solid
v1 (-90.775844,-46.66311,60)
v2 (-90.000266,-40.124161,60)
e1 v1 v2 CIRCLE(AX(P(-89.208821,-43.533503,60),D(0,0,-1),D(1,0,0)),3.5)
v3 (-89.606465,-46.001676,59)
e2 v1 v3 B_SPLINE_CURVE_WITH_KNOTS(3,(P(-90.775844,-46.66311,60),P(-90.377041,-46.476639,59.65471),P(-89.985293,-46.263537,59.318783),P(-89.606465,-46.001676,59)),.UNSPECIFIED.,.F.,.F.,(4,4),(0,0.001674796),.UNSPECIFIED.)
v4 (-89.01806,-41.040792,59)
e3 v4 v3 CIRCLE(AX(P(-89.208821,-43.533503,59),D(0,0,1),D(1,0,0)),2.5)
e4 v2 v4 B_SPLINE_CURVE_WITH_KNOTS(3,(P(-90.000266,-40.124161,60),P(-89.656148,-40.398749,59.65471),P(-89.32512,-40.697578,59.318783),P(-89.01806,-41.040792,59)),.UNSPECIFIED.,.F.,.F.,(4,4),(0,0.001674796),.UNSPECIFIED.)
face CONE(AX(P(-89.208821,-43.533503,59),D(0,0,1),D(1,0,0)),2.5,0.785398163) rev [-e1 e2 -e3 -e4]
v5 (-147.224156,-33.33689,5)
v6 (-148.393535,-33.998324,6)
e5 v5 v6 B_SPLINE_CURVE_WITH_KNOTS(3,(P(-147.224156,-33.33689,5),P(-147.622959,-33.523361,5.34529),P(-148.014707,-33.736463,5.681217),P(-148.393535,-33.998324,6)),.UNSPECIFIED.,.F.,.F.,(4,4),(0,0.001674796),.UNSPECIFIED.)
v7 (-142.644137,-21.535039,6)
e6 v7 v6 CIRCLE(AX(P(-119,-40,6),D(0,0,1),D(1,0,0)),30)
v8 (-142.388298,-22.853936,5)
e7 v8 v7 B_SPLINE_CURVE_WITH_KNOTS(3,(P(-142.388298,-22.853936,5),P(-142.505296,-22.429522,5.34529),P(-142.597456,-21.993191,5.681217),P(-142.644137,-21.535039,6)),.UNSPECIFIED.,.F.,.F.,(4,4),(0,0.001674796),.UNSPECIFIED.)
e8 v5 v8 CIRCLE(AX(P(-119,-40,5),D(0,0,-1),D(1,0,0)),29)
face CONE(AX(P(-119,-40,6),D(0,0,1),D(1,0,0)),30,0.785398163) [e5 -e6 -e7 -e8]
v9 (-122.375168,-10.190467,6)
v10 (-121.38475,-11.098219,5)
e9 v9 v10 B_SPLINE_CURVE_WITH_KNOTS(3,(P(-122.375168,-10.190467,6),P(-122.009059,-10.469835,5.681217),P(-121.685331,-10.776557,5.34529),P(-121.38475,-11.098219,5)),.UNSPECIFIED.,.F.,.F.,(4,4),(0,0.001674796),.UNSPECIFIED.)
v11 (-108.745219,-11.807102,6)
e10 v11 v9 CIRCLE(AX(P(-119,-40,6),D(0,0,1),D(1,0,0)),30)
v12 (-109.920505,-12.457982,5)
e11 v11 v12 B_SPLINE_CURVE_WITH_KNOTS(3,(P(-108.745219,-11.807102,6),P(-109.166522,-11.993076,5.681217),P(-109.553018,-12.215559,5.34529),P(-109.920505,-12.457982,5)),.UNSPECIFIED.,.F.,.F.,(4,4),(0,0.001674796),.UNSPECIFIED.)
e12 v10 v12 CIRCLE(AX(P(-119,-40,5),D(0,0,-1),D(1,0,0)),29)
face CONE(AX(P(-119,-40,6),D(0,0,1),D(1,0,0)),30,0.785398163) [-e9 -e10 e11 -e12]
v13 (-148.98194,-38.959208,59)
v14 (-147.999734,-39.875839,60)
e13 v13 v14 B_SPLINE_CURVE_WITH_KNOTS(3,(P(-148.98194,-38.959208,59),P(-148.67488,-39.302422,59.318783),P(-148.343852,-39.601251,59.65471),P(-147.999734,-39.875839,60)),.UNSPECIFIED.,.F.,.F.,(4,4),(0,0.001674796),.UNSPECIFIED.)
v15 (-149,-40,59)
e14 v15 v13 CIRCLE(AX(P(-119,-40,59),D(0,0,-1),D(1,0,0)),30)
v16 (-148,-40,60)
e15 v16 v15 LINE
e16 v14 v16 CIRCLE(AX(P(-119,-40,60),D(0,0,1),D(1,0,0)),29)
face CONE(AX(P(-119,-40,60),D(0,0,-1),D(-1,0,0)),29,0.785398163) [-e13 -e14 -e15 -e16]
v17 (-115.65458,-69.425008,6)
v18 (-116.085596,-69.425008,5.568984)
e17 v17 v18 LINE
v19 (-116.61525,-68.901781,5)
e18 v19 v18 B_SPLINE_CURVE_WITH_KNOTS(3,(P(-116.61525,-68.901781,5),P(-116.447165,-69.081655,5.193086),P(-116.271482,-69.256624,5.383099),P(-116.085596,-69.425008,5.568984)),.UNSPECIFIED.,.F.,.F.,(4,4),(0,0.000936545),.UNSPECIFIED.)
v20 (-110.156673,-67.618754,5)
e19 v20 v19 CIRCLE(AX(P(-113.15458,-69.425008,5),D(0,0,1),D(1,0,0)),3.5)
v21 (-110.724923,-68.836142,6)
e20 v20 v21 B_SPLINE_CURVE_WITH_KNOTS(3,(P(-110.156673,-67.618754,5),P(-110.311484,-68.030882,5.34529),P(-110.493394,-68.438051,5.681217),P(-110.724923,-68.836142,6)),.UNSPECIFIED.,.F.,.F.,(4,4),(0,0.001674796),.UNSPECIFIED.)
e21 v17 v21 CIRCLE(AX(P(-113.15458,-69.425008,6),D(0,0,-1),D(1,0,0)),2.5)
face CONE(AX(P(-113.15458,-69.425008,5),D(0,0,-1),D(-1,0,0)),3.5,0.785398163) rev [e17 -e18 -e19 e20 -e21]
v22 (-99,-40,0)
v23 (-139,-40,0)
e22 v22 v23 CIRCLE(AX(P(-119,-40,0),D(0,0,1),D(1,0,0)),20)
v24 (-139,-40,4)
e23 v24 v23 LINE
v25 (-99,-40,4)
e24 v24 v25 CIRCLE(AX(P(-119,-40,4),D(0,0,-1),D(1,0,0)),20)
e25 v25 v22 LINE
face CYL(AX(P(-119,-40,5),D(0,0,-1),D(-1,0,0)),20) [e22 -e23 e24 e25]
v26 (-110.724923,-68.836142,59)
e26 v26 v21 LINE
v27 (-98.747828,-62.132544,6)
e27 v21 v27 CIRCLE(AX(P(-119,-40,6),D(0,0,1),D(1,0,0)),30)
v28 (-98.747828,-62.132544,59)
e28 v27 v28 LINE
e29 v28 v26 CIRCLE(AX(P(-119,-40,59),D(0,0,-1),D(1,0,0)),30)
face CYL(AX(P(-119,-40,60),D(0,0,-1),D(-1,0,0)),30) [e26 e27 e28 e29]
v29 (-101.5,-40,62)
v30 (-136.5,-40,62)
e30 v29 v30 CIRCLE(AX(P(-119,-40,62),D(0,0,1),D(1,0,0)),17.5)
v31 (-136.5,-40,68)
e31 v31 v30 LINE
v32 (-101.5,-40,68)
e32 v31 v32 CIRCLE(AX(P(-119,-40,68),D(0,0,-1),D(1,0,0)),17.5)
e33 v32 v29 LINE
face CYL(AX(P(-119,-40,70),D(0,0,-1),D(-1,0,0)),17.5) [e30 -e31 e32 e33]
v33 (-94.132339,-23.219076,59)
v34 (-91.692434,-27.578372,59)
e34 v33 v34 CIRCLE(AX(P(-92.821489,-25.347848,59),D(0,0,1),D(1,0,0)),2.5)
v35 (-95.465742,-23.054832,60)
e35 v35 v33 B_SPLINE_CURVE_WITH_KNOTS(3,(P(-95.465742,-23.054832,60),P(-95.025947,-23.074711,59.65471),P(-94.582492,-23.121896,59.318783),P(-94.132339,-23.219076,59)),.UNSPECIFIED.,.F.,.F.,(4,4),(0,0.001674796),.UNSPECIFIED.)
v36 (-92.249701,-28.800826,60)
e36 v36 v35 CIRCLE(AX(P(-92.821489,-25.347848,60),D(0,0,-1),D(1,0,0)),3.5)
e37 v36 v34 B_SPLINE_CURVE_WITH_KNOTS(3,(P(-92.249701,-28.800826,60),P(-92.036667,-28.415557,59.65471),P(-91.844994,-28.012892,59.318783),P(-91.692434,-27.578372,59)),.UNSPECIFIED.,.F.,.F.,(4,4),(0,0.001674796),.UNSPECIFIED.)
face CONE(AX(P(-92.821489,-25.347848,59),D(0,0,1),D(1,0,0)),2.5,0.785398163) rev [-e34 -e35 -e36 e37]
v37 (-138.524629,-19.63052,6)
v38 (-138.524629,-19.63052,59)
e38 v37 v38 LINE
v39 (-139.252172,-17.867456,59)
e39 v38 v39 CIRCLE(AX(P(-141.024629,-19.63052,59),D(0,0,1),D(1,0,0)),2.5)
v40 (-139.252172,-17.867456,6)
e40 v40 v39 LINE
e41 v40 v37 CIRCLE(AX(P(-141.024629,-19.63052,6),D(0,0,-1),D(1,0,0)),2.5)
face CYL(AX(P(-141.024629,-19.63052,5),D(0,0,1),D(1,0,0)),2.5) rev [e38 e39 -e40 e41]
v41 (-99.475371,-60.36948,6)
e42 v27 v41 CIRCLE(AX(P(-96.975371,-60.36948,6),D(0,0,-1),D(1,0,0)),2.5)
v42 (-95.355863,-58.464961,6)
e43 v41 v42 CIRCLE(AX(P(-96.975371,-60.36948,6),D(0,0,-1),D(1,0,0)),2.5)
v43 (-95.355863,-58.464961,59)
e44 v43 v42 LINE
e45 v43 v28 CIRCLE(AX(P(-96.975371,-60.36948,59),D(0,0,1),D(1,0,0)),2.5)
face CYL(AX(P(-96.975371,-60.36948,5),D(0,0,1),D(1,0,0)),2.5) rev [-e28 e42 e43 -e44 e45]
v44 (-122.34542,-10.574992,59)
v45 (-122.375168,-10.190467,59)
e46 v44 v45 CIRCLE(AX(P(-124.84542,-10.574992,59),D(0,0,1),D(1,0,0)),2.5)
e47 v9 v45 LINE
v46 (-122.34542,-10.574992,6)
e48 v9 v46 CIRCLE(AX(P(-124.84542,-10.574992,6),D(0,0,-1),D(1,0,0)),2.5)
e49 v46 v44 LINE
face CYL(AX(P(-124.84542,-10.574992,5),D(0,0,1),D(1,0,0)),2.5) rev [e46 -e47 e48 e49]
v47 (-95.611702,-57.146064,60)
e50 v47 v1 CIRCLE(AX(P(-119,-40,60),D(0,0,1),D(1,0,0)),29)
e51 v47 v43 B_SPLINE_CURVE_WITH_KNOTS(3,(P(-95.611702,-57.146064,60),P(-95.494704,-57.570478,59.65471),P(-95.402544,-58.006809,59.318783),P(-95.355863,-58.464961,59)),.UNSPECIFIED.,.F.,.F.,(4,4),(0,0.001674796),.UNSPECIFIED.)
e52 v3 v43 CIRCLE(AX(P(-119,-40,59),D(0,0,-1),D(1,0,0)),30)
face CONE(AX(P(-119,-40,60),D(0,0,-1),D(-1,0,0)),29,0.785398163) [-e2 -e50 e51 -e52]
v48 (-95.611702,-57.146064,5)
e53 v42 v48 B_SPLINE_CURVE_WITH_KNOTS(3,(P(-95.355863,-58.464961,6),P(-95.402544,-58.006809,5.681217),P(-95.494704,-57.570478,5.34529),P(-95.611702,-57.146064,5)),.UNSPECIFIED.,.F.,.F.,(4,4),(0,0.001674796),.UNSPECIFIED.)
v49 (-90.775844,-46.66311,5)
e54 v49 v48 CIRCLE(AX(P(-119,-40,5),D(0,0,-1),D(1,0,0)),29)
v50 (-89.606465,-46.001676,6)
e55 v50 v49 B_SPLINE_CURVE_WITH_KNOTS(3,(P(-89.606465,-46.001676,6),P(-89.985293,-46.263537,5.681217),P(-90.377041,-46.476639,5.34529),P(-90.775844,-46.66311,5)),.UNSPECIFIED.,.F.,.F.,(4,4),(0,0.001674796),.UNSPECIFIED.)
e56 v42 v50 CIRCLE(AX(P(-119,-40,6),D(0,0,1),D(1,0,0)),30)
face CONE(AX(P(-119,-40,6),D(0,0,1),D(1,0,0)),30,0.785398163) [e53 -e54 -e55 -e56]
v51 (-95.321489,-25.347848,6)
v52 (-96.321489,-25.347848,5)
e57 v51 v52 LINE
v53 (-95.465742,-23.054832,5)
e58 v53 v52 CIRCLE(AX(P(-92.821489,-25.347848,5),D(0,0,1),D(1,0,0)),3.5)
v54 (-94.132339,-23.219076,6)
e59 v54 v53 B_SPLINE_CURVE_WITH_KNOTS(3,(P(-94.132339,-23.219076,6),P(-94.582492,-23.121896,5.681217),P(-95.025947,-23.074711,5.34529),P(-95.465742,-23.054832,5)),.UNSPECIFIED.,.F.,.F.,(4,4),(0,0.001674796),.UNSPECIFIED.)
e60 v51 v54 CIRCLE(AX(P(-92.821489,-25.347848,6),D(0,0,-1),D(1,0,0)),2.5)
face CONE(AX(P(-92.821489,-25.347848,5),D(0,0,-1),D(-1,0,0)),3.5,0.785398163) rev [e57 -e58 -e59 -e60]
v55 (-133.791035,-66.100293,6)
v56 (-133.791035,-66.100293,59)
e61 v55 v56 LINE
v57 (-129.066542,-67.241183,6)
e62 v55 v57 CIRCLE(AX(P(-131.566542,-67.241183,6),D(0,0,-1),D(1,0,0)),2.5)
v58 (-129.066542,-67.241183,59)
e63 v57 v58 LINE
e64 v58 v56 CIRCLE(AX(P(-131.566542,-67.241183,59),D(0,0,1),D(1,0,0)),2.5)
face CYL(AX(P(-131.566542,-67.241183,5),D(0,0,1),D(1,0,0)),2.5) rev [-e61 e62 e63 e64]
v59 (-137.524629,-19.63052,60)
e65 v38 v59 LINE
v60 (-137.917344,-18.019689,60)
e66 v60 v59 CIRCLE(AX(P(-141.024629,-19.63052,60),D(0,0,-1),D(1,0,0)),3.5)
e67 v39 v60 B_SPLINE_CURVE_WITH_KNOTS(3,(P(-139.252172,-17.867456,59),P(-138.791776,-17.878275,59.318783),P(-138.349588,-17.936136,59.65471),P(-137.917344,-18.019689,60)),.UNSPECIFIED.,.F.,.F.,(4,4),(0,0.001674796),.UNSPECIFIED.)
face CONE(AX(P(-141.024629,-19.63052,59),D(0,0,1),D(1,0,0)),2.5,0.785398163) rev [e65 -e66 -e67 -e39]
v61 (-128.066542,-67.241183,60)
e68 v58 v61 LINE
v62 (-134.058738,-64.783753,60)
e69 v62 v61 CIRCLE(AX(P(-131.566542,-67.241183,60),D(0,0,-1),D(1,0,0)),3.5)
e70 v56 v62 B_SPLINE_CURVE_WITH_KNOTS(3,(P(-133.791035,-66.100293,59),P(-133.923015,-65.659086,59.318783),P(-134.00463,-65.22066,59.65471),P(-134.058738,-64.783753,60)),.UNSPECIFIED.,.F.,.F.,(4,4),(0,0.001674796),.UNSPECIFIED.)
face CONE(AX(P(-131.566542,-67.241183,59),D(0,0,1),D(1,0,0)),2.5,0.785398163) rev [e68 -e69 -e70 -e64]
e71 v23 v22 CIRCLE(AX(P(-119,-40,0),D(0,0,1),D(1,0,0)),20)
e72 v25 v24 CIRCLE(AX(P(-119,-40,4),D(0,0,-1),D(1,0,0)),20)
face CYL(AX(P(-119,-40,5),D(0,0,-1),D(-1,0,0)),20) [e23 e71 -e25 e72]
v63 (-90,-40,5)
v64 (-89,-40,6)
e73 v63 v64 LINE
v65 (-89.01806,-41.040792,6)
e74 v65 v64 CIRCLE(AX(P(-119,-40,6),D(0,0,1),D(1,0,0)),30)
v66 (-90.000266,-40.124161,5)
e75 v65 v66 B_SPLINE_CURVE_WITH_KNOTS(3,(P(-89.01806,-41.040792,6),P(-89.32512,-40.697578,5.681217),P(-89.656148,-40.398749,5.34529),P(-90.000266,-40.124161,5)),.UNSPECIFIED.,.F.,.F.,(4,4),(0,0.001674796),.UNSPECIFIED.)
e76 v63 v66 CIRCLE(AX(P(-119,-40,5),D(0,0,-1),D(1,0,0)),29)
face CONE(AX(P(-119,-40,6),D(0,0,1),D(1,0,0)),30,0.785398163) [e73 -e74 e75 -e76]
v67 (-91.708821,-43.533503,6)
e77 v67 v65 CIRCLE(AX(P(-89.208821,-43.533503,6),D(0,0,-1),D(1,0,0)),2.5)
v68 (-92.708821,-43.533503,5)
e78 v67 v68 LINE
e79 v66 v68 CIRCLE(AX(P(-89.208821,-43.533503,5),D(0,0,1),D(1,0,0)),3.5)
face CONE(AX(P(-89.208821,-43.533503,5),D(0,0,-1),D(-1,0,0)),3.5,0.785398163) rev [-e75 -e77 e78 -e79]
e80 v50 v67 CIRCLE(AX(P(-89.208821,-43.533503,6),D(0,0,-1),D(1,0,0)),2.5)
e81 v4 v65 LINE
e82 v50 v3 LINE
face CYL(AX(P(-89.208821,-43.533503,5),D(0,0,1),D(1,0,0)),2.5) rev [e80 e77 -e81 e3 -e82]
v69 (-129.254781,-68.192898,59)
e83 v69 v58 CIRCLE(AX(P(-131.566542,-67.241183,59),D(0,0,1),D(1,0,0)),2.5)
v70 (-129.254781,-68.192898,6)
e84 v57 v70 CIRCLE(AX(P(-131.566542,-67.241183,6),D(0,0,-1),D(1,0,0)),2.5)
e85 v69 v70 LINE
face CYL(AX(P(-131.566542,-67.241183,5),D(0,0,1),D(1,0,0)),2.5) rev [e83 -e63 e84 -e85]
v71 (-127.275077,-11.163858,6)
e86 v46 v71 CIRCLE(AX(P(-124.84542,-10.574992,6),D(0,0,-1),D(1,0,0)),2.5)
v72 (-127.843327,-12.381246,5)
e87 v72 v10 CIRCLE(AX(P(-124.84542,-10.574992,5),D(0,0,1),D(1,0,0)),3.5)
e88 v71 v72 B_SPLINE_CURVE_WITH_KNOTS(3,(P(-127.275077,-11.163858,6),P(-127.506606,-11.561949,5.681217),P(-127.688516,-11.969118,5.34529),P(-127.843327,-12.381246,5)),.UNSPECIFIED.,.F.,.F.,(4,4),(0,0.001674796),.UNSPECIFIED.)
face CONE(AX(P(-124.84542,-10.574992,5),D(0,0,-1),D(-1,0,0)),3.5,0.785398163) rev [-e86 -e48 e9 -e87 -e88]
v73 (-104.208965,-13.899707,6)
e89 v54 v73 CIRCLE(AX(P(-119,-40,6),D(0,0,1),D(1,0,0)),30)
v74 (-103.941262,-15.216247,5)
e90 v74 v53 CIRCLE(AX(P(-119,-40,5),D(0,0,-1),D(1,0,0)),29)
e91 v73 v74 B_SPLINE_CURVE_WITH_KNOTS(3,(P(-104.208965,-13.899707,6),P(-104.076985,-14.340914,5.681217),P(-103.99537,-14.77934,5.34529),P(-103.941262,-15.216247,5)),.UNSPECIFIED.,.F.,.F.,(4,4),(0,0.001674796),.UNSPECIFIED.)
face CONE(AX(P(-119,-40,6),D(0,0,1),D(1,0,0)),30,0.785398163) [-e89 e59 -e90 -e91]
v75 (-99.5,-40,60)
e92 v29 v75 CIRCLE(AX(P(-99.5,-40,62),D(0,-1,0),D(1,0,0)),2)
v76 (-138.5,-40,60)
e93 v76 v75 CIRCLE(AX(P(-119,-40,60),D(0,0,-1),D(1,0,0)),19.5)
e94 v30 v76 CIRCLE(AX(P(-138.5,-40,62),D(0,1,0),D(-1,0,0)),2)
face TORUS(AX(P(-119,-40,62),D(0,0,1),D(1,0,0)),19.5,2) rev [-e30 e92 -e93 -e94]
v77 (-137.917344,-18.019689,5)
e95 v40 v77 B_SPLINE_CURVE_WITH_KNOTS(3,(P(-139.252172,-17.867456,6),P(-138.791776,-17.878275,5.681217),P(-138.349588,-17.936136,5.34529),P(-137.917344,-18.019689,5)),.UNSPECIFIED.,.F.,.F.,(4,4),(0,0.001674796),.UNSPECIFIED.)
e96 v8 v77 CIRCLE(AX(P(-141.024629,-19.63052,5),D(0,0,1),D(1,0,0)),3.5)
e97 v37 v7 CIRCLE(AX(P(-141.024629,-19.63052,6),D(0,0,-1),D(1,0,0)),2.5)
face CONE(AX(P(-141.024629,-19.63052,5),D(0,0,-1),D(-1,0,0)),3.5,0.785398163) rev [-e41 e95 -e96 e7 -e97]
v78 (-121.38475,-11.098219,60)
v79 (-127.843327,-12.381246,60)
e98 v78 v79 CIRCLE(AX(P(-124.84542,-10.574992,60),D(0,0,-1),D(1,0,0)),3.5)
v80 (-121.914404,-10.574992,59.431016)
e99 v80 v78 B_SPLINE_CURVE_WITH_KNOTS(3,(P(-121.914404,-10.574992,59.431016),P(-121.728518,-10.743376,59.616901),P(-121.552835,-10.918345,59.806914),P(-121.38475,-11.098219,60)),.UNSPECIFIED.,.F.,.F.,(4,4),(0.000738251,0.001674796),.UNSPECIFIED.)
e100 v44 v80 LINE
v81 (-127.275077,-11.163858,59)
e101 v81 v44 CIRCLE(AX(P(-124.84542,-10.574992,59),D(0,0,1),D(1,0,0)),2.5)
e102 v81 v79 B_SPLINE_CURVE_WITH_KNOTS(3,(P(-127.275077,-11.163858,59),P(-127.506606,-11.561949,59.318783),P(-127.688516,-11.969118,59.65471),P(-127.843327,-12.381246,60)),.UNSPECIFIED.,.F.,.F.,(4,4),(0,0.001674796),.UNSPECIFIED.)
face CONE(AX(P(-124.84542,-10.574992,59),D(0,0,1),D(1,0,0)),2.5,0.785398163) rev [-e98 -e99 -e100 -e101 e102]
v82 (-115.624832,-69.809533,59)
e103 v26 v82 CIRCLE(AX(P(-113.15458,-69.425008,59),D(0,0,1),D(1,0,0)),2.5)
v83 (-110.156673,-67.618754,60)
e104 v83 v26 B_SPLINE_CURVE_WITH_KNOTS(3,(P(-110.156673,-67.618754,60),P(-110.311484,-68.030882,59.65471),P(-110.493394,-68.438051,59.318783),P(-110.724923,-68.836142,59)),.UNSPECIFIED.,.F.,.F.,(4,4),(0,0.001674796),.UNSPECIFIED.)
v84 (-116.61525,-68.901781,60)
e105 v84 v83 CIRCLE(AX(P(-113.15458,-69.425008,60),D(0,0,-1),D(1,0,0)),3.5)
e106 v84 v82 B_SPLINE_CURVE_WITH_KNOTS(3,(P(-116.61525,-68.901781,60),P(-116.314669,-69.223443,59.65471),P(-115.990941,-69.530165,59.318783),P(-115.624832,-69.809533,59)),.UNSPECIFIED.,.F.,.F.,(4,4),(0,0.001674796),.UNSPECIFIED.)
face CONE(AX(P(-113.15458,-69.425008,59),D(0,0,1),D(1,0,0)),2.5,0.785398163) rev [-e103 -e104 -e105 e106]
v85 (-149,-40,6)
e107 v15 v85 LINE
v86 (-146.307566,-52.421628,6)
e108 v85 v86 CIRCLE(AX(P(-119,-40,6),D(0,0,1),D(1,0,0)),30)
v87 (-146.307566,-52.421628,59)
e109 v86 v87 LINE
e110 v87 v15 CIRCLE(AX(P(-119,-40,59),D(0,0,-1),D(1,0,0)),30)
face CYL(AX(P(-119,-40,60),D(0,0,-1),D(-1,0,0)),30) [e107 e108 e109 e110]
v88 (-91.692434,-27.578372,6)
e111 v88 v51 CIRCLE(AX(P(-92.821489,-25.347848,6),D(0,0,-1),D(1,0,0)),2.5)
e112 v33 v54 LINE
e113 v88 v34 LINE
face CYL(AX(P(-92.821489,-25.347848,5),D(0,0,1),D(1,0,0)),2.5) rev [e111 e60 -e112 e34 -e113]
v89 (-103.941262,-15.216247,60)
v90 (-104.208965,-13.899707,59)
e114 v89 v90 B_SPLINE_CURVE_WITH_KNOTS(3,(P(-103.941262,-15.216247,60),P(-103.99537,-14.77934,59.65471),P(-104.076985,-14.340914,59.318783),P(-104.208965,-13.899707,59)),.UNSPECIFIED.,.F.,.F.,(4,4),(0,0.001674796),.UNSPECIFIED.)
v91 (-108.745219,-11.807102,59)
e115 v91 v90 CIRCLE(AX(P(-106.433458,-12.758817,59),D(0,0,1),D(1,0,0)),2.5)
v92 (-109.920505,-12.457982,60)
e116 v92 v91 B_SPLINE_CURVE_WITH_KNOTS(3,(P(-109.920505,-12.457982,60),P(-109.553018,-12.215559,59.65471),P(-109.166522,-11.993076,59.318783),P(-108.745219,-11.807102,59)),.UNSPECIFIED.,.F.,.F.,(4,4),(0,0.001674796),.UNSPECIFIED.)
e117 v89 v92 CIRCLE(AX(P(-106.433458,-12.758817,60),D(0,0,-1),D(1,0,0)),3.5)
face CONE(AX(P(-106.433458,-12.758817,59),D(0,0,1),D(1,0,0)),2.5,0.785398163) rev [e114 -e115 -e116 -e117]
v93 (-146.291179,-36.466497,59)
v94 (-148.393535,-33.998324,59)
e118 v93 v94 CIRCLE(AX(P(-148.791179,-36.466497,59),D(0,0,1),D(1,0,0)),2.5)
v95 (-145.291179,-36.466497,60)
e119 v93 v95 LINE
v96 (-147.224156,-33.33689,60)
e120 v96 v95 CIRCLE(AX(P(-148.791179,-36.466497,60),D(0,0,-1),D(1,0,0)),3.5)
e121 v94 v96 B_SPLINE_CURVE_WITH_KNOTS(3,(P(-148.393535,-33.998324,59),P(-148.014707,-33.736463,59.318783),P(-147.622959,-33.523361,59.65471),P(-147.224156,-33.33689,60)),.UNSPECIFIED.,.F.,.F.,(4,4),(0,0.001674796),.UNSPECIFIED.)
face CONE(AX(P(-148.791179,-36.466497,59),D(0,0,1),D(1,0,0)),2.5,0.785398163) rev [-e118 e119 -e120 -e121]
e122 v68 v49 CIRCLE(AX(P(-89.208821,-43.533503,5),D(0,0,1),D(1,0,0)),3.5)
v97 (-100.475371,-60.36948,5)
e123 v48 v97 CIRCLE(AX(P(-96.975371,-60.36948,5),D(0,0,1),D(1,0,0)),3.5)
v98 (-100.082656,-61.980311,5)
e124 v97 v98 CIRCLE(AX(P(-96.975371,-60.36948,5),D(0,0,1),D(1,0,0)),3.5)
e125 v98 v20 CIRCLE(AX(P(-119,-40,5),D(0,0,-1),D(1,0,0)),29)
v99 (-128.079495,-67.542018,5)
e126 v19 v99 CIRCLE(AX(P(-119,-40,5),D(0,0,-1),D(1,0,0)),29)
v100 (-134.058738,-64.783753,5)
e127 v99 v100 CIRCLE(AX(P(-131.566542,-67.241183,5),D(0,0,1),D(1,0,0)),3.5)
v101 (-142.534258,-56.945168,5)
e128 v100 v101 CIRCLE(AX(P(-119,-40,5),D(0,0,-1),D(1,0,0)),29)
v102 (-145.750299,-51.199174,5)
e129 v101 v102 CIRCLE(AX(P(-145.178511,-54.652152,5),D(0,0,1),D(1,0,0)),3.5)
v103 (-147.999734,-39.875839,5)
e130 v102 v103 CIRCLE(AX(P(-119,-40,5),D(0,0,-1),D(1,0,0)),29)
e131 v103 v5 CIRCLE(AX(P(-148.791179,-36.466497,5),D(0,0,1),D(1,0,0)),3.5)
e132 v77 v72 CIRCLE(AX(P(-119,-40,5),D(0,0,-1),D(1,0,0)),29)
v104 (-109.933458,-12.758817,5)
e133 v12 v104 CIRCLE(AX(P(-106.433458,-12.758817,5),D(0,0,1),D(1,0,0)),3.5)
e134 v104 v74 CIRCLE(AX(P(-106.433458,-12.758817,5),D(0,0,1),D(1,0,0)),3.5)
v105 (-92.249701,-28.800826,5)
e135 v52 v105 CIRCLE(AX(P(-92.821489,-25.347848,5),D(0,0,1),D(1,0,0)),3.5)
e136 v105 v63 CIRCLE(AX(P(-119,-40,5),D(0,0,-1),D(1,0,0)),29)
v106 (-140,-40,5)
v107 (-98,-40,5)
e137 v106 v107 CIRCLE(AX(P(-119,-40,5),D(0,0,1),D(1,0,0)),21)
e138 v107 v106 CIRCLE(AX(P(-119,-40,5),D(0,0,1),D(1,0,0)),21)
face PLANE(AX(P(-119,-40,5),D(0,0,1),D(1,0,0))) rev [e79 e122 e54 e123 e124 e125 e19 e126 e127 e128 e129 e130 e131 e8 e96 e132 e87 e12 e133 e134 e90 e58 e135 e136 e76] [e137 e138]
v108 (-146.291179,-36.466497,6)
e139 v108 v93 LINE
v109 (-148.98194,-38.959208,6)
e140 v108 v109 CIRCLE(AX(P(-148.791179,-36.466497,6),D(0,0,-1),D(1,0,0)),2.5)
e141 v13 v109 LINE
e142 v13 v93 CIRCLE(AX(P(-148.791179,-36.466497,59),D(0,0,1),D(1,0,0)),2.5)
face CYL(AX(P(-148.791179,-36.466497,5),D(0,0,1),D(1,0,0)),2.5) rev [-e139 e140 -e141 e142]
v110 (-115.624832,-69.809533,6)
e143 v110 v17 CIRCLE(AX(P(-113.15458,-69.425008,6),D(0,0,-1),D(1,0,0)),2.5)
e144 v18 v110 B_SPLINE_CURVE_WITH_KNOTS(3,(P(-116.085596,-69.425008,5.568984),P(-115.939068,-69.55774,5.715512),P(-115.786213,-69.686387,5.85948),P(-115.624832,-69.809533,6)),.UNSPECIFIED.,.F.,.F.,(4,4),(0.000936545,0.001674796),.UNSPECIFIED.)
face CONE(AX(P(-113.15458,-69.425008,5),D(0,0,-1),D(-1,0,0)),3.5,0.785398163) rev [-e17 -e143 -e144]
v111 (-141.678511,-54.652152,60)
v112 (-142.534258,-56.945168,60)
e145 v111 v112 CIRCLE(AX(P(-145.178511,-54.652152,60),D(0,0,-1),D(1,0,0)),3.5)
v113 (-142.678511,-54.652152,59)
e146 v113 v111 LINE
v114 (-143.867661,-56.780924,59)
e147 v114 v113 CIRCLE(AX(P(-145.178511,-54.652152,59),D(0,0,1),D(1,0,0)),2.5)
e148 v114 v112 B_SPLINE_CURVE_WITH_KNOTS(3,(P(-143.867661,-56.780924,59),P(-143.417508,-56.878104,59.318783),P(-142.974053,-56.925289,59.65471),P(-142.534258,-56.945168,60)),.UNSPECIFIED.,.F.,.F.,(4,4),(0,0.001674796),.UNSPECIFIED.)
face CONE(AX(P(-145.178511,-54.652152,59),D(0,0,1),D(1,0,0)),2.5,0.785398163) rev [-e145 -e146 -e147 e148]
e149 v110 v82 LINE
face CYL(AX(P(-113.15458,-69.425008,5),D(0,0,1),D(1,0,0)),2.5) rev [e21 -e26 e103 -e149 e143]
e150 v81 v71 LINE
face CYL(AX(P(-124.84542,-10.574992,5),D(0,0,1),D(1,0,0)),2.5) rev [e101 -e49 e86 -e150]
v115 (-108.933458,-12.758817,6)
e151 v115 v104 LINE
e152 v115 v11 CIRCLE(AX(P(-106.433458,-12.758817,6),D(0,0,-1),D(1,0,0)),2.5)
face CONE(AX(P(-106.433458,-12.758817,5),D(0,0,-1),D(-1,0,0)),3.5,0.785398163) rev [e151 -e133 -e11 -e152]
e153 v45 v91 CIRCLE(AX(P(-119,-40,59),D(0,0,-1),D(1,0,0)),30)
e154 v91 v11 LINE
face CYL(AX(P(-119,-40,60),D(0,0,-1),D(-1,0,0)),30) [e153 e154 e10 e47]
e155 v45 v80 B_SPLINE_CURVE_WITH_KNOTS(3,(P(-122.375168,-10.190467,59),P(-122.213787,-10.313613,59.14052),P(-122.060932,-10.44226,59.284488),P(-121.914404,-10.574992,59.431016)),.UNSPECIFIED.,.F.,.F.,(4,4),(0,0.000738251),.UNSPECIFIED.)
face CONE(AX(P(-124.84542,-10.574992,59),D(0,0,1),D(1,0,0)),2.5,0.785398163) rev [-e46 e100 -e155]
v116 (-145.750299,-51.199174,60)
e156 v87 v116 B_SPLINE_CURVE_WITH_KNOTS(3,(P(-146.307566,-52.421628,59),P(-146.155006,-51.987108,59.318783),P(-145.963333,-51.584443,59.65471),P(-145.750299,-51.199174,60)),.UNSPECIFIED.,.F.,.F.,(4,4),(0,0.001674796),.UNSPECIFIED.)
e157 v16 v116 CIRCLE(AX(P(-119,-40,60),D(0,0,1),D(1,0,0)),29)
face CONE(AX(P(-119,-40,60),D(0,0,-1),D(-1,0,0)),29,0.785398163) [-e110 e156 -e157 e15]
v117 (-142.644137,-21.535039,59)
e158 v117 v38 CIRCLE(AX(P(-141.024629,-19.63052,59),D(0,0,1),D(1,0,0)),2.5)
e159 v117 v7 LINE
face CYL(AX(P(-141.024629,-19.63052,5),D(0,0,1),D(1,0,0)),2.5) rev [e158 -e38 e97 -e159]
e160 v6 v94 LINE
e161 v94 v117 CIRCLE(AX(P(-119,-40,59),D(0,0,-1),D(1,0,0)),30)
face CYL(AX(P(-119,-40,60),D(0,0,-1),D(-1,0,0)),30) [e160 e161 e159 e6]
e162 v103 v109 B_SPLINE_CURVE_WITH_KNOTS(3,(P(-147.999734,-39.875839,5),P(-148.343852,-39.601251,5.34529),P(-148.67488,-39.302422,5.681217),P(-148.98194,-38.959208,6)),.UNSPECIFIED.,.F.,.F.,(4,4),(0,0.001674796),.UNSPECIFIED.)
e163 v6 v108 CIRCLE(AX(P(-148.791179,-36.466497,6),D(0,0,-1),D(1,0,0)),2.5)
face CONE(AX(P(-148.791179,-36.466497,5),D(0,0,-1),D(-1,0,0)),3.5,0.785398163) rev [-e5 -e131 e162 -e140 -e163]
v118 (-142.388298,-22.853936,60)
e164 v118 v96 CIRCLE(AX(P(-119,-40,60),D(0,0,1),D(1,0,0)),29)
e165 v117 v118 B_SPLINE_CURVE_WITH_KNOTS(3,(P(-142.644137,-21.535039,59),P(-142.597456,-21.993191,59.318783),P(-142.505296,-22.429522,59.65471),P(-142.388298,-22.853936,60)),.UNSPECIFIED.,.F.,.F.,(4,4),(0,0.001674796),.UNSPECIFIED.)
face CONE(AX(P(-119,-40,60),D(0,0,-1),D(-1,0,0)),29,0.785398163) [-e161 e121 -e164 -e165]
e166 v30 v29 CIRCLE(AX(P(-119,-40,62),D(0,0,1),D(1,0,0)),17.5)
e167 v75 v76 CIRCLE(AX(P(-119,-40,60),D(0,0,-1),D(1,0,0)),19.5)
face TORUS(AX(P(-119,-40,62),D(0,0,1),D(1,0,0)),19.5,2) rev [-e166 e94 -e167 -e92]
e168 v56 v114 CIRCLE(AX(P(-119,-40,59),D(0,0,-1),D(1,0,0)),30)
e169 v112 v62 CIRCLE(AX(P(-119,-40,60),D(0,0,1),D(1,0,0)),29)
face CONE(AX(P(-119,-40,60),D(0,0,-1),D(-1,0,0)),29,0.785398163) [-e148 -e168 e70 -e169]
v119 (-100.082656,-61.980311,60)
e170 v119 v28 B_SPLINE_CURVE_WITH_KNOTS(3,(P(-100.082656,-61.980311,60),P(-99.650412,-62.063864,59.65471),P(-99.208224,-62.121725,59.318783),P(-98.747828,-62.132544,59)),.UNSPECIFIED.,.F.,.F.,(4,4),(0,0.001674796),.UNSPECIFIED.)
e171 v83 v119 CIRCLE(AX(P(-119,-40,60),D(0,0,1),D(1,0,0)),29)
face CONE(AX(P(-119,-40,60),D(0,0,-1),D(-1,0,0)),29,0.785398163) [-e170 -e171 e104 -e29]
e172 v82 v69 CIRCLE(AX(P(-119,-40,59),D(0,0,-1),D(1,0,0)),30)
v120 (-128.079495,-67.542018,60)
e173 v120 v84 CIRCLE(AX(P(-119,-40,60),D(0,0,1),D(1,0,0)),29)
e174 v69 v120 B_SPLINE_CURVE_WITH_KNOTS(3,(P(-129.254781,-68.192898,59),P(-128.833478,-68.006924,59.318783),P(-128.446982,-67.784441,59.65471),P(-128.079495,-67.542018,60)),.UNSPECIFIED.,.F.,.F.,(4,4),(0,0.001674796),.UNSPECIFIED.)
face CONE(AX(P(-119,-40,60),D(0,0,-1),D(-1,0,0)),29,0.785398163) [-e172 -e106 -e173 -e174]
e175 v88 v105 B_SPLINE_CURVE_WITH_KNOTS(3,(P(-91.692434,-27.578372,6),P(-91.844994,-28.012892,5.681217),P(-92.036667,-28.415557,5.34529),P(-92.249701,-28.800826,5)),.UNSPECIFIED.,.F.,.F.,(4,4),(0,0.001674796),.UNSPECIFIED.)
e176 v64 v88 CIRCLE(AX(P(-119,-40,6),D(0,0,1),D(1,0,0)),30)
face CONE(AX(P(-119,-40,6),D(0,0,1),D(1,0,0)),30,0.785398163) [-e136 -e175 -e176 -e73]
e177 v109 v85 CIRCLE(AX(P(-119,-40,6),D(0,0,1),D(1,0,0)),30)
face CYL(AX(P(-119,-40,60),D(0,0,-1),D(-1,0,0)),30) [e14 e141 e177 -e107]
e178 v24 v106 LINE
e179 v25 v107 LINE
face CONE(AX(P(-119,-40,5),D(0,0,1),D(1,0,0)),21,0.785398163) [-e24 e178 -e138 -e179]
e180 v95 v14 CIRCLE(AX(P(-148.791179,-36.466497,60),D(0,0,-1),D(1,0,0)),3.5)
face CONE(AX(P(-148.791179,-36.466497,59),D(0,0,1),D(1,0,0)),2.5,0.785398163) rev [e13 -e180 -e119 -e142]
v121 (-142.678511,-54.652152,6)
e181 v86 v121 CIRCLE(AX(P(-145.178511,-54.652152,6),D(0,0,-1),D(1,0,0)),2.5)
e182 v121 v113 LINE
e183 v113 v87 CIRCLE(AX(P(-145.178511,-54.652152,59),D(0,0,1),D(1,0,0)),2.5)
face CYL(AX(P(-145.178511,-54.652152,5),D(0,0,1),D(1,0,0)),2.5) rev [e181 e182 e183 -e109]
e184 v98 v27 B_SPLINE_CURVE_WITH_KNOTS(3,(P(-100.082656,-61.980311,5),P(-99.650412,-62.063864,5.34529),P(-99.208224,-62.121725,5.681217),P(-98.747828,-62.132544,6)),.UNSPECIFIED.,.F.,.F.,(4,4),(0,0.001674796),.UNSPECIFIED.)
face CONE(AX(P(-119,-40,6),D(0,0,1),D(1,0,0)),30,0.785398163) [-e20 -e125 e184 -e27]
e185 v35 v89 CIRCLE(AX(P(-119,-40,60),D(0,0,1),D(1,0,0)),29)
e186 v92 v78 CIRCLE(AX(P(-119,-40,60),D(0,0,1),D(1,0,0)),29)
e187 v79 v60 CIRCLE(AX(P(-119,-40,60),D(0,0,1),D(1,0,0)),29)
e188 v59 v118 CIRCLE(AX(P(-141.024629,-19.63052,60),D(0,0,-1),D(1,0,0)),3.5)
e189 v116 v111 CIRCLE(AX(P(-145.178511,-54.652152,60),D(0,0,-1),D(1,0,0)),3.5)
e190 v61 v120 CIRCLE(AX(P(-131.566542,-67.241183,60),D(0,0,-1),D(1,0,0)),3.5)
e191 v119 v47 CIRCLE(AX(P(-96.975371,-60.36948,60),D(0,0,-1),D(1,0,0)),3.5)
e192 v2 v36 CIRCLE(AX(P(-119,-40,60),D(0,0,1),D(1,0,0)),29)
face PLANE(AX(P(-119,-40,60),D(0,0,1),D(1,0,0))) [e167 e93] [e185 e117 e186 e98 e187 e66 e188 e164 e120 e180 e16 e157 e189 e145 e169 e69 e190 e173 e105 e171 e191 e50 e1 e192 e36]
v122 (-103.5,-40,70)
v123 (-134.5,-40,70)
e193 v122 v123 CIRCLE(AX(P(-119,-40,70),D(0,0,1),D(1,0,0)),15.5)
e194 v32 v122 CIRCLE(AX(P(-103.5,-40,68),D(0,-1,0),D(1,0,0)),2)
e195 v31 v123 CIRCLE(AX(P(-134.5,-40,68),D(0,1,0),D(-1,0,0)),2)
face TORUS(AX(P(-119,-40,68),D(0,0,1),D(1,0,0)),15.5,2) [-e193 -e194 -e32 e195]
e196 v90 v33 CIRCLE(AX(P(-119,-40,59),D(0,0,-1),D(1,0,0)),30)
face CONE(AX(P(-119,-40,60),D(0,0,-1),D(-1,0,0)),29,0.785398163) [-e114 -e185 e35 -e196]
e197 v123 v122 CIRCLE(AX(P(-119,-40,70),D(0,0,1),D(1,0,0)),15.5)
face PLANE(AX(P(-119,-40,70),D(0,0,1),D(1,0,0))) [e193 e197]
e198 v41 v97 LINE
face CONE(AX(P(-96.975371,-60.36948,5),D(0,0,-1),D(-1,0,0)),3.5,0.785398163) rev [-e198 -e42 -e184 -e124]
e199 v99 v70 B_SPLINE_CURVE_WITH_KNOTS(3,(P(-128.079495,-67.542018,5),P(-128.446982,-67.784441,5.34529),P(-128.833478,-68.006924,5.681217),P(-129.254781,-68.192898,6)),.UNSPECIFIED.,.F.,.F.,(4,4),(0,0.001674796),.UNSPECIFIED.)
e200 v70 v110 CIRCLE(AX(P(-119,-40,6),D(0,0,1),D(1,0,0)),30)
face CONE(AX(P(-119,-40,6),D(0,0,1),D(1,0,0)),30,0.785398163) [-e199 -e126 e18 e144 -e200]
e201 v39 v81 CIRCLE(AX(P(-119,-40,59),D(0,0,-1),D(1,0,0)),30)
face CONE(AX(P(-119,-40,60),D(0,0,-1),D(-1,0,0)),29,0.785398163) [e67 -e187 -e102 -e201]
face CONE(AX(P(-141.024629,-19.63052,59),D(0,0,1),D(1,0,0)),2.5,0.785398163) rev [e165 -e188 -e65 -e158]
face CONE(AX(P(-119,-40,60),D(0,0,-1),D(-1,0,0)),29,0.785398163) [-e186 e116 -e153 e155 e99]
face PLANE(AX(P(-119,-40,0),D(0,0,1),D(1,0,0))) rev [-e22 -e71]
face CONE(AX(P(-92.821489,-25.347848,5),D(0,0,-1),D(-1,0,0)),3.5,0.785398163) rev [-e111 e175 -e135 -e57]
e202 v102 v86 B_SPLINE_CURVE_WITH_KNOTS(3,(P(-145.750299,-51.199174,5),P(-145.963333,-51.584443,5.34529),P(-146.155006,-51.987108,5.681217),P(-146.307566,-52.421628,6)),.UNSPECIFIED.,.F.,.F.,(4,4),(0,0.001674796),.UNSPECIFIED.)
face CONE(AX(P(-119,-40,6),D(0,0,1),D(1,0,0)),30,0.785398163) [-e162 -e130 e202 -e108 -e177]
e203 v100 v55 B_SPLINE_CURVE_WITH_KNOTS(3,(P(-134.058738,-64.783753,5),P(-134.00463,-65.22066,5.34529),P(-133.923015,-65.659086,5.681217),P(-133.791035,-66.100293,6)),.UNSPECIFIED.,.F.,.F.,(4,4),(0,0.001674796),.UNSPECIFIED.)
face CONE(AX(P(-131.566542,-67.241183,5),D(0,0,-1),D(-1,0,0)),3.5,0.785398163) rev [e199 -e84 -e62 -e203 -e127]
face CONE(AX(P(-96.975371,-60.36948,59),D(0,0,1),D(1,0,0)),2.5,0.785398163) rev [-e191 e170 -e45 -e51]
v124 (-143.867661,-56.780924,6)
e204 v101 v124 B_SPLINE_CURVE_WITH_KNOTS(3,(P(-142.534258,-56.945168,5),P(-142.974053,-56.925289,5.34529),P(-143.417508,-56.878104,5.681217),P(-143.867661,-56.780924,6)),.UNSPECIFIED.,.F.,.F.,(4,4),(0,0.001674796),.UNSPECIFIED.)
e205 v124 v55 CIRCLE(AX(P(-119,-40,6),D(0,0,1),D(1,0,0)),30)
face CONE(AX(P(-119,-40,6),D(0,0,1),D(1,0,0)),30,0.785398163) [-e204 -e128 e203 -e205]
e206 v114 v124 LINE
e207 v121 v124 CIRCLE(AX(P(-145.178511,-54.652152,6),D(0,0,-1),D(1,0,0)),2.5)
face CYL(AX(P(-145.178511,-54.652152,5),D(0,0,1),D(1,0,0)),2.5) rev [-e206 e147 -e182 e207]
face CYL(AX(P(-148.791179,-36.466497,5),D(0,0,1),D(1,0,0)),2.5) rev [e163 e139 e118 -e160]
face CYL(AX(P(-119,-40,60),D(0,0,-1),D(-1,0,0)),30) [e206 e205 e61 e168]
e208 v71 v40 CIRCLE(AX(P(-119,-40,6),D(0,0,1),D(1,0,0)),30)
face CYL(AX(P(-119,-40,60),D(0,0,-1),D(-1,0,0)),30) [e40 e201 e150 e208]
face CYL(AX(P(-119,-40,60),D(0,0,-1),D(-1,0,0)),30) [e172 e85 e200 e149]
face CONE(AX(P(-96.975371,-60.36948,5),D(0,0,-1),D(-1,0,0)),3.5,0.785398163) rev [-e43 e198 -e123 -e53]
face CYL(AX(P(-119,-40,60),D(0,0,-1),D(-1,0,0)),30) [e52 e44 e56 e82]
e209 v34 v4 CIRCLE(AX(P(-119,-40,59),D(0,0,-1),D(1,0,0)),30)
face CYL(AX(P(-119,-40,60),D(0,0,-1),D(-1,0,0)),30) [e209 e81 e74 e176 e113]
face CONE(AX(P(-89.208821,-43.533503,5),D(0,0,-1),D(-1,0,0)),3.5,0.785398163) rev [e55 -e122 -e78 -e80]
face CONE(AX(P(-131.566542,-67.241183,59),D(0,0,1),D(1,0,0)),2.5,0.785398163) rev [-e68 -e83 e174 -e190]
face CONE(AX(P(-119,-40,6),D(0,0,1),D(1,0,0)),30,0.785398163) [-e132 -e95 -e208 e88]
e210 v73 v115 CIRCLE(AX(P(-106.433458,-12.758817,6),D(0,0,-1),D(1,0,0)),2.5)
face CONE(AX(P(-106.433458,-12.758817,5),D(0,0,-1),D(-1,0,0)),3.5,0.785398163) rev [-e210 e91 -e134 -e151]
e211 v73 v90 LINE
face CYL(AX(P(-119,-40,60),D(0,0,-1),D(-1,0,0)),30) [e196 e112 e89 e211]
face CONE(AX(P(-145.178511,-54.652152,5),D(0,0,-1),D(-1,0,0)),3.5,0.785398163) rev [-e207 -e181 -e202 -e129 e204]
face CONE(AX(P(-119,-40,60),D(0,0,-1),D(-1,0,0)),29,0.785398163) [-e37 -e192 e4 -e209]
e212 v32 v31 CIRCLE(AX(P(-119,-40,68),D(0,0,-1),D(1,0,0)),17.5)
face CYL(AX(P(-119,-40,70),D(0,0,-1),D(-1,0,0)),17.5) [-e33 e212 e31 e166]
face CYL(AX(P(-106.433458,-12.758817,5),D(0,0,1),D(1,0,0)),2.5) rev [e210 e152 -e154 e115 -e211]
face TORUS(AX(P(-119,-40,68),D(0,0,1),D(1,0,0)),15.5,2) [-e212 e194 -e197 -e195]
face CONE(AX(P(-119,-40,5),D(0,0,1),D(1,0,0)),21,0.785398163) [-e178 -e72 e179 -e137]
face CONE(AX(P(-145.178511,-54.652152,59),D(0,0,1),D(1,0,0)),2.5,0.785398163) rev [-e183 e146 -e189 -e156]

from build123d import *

# Parameters (mm, degrees)
SKETCH1_R           = 20
BOSS_EXTRUDE1_DEPTH = 5
SKETCH2_R           = 30
BOSS_EXTRUDE2_DEPTH = 55
SKETCH3_R           = 2.5
CUT_EXTRUDE1_DEPTH  = 55
CHAMFER1_SIZE       = 1
SKETCH4_R           = 17.5
BOSS_EXTRUDE3_DEPTH = 10
FILLET1_R           = 2


with BuildPart() as part:
    # Sketch1 → Boss-Extrude1 (new body)
    with BuildSketch(Plane.XY):
        with Locations((-119, -40)):
            Circle(SKETCH1_R)
    extrude(amount=BOSS_EXTRUDE1_DEPTH)

    # Sketch2 → Boss-Extrude2 (add)
    with BuildSketch(Plane.XY.offset(5)):
        with Locations((-119, -40)):
            Circle(SKETCH2_R)
    extrude(amount=BOSS_EXTRUDE2_DEPTH)

    # Sketch3 → Cut-Extrude1 (cut)
    with BuildSketch(Plane.XY.offset(60)):
        with Locations((-92.821488811, -25.347848215)):
            Circle(SKETCH3_R)
        with Locations((-89.208820827, -43.533503006)):
            Circle(SKETCH3_R)
        with Locations((-96.975370722, -60.369479748)):
            Circle(SKETCH3_R)
        with Locations((-113.154580412, -69.425007559)):
            Circle(SKETCH3_R)
        with Locations((-131.566541706, -67.241182602)):
            Circle(SKETCH3_R)
        with Locations((-145.178511189, -54.652151785)):
            Circle(SKETCH3_R)
        with Locations((-148.791179173, -36.466496994)):
            Circle(SKETCH3_R)
        with Locations((-141.024629278, -19.630520252)):
            Circle(SKETCH3_R)
        with Locations((-124.845419588, -10.574992441)):
            Circle(SKETCH3_R)
        with Locations((-106.433458294, -12.758817398)):
            Circle(SKETCH3_R)
    extrude(amount=-CUT_EXTRUDE1_DEPTH, mode=Mode.SUBTRACT)

    # Chamfer1
    chamfer1_edges = [part.edges().sort_by_distance(p)[0] for p in [
        (-115.466496994, -10.208820827, 5),
        (-133.652151785, -13.821488811, 5),
        (-146.241182602, -27.433458294, 5),
        (-148.425007559, -45.845419588, 5),
        (-139.369479748, -62.024629278, 5),
        (-122.533503006, -69.791179173, 5),
        (-104.347848215, -66.178511189, 5),
        (-91.758817398, -52.566541706, 5),
        (-89.574992441, -34.154580412, 5),
        (-130.519329897, -64.971084052, 5),
        (-142.99696859, -53.431139136, 5),
        (-146.308580908, -36.760955578, 5),
        (-139.189243504, -21.327976898, 5),
        (-124.358301289, -13.027076404, 5),
        (-98.630520252, -17.975370722, 60),
        (-115.466496994, -10.208820827, 60),
        (-133.652151785, -13.821488811, 60),
        (-146.241182602, -27.433458294, 60),
        (-148.425007559, -45.845419588, 60),
        (-139.369479748, -62.024629278, 60),
        (-122.533503006, -69.791179173, 60),
        (-104.347848215, -66.178511189, 60),
        (-91.758817398, -52.566541706, 60),
        (-89.574992441, -34.154580412, 60),
        (-124.358301289, -13.027076404, 60),
        (-139.189243504, -21.327976898, 60),
        (-146.308580908, -36.760955578, 60),
        (-139, -40, 5),
        (-142.99696859, -53.431139136, 60),
        (-130.519329897, -64.971084052, 60),
        (-113.641698711, -66.972923596, 60),
        (-113.641698711, -66.972923596, 5),
        (-98.810756496, -58.672023102, 60),
        (-98.810756496, -58.672023102, 5),
        (-91.691419092, -43.239044422, 60),
        (-91.691419092, -43.239044422, 5),
        (-107.480670103, -15.028915948, 60),
        (-107.480670103, -15.028915948, 5),
        (-95.00303141, -26.568860864, 60),
        (-95.00303141, -26.568860864, 5),
        (-98.630520252, -17.975370722, 5),
    ]]
    chamfer(chamfer1_edges, length=CHAMFER1_SIZE)

    # Sketch4 → Boss-Extrude3 (add)
    with BuildSketch(Plane.XY.offset(60)):
        with Locations((-119, -40)):
            Circle(SKETCH4_R)
    extrude(amount=BOSS_EXTRUDE3_DEPTH)

    # Fillet1
    fillet1_edges = [part.edges().sort_by_distance(p)[0] for p in [
        (-136.5, -40, 60),
        (-136.5, -40, 70),
    ]]
    fillet(fillet1_edges, radius=FILLET1_R)


solid = part.part
